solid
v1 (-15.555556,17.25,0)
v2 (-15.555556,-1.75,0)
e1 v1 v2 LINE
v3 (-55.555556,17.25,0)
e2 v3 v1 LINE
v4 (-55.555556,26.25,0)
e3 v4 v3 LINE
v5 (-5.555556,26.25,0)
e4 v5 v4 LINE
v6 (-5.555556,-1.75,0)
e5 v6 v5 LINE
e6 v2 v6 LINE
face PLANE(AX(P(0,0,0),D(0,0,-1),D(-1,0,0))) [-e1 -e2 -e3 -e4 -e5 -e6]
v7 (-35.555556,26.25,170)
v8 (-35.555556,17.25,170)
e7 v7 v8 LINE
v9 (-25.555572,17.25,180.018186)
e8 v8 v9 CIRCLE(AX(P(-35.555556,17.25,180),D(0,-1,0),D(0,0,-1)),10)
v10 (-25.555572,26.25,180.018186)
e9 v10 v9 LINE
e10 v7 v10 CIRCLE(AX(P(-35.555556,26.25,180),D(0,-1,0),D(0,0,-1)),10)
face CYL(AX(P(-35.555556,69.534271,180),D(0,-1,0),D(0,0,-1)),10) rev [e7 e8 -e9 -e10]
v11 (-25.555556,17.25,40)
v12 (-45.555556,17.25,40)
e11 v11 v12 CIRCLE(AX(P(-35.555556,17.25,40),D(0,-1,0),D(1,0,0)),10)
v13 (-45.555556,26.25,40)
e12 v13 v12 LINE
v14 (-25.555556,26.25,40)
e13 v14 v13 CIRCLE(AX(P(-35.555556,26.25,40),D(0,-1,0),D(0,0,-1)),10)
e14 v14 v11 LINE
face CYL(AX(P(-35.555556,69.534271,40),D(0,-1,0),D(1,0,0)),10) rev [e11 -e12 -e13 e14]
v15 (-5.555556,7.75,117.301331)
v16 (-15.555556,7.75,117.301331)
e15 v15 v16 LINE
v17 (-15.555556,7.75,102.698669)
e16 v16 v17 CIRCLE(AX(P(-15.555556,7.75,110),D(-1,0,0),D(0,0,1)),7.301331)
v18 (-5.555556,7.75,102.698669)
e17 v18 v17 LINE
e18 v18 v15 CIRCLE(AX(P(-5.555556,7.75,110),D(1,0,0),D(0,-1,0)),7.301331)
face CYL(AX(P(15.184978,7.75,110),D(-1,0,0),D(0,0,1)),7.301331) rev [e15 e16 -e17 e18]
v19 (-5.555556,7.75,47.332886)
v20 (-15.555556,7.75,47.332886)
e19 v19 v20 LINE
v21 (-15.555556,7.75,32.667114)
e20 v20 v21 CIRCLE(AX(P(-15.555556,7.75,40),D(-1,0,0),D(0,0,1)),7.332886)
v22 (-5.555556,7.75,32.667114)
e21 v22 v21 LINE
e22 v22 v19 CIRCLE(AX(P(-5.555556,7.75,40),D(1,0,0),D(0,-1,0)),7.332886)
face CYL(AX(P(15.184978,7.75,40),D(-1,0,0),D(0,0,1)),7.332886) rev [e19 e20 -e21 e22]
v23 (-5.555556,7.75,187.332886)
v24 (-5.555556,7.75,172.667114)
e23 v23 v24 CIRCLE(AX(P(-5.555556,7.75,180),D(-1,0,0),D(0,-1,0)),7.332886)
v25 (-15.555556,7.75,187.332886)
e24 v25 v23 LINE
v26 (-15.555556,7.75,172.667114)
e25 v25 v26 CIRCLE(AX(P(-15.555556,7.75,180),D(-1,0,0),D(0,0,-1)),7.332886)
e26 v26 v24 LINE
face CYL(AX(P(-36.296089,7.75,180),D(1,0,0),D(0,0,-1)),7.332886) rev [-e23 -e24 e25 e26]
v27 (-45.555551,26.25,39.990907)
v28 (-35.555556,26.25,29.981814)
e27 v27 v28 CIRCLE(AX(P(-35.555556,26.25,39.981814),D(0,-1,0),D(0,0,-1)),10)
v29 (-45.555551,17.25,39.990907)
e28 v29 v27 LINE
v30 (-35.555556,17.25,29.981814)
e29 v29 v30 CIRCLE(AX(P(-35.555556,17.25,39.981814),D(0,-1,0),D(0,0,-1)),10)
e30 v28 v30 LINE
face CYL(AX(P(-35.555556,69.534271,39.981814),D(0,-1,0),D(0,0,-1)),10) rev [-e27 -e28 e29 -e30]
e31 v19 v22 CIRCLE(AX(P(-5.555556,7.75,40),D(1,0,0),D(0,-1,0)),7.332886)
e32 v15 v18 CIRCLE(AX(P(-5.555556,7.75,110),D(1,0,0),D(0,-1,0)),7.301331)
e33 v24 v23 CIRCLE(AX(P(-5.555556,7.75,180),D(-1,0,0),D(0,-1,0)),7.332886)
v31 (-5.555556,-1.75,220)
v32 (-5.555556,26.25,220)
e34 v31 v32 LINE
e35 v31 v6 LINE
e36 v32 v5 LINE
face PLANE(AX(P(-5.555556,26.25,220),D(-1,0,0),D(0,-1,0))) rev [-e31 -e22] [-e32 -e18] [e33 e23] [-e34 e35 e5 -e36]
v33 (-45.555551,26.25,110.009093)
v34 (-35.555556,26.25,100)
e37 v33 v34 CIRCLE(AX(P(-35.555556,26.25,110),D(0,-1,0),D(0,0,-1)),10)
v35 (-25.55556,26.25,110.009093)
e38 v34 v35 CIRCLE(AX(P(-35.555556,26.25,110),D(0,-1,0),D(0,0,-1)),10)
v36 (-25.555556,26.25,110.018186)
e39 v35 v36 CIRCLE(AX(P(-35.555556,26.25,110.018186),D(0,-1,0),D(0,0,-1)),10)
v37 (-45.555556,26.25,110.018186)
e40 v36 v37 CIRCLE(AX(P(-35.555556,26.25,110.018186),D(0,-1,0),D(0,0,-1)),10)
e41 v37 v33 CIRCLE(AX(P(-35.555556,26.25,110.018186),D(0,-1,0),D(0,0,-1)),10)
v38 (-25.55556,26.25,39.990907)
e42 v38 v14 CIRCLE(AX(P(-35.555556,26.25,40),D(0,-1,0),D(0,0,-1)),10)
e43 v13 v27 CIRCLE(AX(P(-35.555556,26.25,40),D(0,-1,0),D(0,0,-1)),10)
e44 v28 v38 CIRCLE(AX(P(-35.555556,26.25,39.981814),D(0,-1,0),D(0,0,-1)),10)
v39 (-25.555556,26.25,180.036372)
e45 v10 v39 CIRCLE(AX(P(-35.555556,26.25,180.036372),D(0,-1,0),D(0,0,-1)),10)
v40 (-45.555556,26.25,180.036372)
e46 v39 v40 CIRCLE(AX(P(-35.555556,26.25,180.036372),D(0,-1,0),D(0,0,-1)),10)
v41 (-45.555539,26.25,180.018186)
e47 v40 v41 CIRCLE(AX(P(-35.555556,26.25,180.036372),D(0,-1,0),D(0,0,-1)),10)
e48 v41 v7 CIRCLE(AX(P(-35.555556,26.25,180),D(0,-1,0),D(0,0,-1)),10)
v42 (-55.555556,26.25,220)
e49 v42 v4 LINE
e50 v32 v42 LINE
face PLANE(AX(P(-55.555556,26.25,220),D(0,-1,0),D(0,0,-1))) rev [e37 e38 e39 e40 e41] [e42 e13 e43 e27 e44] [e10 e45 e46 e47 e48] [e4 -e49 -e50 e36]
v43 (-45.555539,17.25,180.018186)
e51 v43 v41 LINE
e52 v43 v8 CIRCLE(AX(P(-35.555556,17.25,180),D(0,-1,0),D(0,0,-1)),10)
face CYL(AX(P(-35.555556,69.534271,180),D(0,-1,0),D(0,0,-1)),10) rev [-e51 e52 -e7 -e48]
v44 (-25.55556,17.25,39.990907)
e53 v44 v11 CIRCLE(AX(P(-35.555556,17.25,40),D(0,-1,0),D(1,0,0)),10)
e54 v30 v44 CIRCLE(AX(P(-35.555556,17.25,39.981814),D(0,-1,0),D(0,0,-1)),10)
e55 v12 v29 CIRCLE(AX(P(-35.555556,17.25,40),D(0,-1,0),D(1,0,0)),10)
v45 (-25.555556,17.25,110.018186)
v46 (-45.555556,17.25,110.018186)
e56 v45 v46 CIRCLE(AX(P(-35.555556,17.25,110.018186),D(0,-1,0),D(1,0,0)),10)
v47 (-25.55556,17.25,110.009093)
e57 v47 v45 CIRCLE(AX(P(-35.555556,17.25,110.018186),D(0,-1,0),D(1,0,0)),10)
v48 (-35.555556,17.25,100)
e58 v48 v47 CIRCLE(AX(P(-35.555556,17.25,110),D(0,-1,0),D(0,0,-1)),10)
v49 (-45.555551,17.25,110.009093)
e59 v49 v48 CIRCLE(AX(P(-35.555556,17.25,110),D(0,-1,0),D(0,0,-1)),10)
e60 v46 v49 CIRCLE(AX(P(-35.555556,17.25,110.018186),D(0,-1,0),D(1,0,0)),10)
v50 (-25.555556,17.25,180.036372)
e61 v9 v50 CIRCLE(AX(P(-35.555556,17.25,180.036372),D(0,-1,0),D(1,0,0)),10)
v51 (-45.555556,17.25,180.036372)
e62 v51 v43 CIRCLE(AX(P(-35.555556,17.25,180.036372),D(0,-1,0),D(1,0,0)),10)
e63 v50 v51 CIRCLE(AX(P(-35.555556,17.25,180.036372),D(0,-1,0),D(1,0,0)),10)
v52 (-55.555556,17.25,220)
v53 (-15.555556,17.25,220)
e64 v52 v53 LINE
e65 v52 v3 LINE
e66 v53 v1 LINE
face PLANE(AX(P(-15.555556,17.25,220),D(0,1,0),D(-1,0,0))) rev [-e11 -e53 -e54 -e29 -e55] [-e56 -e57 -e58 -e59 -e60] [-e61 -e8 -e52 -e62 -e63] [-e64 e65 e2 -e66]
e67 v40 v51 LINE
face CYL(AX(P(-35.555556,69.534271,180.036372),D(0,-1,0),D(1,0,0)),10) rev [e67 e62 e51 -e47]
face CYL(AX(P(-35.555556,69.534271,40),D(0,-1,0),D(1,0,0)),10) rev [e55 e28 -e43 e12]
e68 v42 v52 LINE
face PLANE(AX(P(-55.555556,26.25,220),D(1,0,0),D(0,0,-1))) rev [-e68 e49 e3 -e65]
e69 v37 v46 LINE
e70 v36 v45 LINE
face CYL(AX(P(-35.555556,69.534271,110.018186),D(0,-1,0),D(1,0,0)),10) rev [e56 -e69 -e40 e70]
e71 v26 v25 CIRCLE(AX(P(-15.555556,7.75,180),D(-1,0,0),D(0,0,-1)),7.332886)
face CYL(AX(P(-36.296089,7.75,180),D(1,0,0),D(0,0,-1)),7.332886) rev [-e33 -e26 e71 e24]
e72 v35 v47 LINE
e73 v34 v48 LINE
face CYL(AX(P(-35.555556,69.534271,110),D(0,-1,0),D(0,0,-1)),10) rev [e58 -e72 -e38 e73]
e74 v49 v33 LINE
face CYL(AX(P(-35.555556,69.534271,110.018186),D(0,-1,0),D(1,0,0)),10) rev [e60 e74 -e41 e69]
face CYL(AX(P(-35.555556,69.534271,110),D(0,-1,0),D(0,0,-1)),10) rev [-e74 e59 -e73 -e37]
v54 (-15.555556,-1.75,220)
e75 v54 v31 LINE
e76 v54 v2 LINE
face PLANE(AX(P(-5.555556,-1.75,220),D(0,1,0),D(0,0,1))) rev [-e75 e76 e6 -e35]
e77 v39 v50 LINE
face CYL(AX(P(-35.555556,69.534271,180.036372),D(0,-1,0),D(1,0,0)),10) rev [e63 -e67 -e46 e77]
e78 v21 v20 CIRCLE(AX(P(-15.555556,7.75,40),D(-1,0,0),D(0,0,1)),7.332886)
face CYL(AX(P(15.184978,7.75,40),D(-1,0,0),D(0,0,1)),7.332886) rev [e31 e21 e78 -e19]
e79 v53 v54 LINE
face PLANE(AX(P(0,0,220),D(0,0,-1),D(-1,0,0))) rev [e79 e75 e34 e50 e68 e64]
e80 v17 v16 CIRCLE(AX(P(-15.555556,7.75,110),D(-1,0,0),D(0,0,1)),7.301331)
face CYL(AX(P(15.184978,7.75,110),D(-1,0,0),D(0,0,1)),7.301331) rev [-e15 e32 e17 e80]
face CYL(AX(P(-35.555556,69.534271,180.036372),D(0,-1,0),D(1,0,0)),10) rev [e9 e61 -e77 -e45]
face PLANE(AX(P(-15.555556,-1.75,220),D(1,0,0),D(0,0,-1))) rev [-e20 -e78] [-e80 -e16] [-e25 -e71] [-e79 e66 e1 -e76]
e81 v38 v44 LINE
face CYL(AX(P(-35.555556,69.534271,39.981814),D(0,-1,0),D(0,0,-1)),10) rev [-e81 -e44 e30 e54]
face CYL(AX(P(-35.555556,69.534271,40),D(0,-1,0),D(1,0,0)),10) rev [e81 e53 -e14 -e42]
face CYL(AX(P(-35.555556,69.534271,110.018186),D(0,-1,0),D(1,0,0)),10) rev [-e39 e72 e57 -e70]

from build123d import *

# Parameters (mm, degrees)
EXTRUDE_1_DEPTH     = 220
SKETCH_2_R          = 10
CUT_EXTRUDE_1_DEPTH = 24
SKETCH_3_R          = 10
CUT_EXTRUDE_2_DEPTH = 24
SKETCH_4_R          = 7.332886018
SKETCH_4_R_2        = 7.301331484
SKETCH_4_R_3        = 6.603217824
CUT_EXTRUDE_3_DEPTH = 10
CUT_EXTRUDE_START   = -45
SKETCH_5_R          = 7.332886018
SKETCH_5_R_2        = 7.301331484
SKETCH_5_R_3        = 6.603217824
CUT_EXTRUDE_4_DEPTH = 45


with BuildPart() as part:
    # 草图1 → 凸台-拉伸1 (new body)
    with BuildSketch(Plane.XY):
        Polygon((-55.555555556, 26.25), (-5.555555556, 26.25), (-5.555555556, -1.75), (-15.555555556, -1.75), (-15.555555556, 17.25), (-55.555555556, 17.25), align=None)
    extrude(amount=EXTRUDE_1_DEPTH)

    # 草图2 → 切除-拉伸1 (cut)
    with BuildSketch(Plane(origin=(982.792188559, 17.25, -600.126281628), x_dir=(0.9997402704834758, 0, 0.022790163966647386), z_dir=(0, -1, 0))):
        with Locations(Location((-1000.30321436, 803.168334002, 0), (0, 0, 358.694106729))):
            Circle(SKETCH_2_R)
        with Locations(Location((-1001.898940295, 733.168334002, 0), (0, 0, 358.694106729))):
            Circle(SKETCH_2_R)
        with Locations(Location((-1003.49466623, 663.168334002, 0), (0, 0, 358.694106729))):
            Circle(SKETCH_2_R)
        with Locations((-915.325705826, 801.212988999)):
            Circle(SKETCH_2_R)
        with Locations((-916.921431761, 731.212988999)):
            Circle(SKETCH_2_R)
        with Locations((-918.516743239, 661.231170065)):
            Circle(SKETCH_2_R)
    extrude(amount=-CUT_EXTRUDE_1_DEPTH, mode=Mode.SUBTRACT)

    # 草图3 → 切除-拉伸2 (cut)
    with BuildSketch(Plane(origin=(-968.90329967, 17.25, 820.126281628), x_dir=(-0.9997402704834758, 0, -0.022790163966647077), z_dir=(0, -1, 0))):
        with Locations((-1000.30321436, 803.168334002)):
            Circle(SKETCH_3_R)
        with Locations((-1001.898940295, 733.168334002)):
            Circle(SKETCH_3_R)
        with Locations((-1003.49466623, 663.168334002)):
            Circle(SKETCH_3_R)
        with Locations((-915.325705826, 801.212988999)):
            Circle(SKETCH_3_R)
        with Locations((-916.921431761, 731.212988999)):
            Circle(SKETCH_3_R)
        with Locations((-918.516743239, 661.231170065)):
            Circle(SKETCH_3_R)
    extrude(amount=-CUT_EXTRUDE_2_DEPTH, mode=Mode.SUBTRACT)

    # 草图4 → 切除-拉伸3 (cut)
    with BuildSketch(Plane(origin=(-15.555555556, -796.892477777, -600.126281629), x_dir=(0, -1, 0), z_dir=(-1, 0, 0))):
        with Locations(Location((-804.642477777, 640.126281628, 0), (0, 0, 90))):
            Circle(SKETCH_4_R)
        with Locations(Location((-804.642477777, 710.126281628, 0), (0, 0, 90))):
            Circle(SKETCH_4_R_2)
        with Locations(Location((-804.642477777, 780.126281628, 0), (0, 0, 90))):
            Circle(SKETCH_4_R_3)
    extrude(amount=-CUT_EXTRUDE_3_DEPTH, mode=Mode.SUBTRACT)

    # 草图5 → 切除-拉伸4 (cut)
    with BuildSketch(Plane(origin=(29.444444444, -796.892477777, 820.126281629), x_dir=(0, -1, 0), z_dir=(1, 0, 0)).offset(CUT_EXTRUDE_START)):
        with Locations(Location((-804.642477777, 640.126281628, 0), (0, 0, 90))):
            Circle(SKETCH_5_R)
        with Locations(Location((-804.642477777, 710.126281628, 0), (0, 0, 270))):
            Circle(SKETCH_5_R_2)
        with Locations((-804.642477777, 780.126281628)):
            Circle(SKETCH_5_R_3)
    extrude(amount=CUT_EXTRUDE_4_DEPTH, mode=Mode.SUBTRACT)


solid = part.part
